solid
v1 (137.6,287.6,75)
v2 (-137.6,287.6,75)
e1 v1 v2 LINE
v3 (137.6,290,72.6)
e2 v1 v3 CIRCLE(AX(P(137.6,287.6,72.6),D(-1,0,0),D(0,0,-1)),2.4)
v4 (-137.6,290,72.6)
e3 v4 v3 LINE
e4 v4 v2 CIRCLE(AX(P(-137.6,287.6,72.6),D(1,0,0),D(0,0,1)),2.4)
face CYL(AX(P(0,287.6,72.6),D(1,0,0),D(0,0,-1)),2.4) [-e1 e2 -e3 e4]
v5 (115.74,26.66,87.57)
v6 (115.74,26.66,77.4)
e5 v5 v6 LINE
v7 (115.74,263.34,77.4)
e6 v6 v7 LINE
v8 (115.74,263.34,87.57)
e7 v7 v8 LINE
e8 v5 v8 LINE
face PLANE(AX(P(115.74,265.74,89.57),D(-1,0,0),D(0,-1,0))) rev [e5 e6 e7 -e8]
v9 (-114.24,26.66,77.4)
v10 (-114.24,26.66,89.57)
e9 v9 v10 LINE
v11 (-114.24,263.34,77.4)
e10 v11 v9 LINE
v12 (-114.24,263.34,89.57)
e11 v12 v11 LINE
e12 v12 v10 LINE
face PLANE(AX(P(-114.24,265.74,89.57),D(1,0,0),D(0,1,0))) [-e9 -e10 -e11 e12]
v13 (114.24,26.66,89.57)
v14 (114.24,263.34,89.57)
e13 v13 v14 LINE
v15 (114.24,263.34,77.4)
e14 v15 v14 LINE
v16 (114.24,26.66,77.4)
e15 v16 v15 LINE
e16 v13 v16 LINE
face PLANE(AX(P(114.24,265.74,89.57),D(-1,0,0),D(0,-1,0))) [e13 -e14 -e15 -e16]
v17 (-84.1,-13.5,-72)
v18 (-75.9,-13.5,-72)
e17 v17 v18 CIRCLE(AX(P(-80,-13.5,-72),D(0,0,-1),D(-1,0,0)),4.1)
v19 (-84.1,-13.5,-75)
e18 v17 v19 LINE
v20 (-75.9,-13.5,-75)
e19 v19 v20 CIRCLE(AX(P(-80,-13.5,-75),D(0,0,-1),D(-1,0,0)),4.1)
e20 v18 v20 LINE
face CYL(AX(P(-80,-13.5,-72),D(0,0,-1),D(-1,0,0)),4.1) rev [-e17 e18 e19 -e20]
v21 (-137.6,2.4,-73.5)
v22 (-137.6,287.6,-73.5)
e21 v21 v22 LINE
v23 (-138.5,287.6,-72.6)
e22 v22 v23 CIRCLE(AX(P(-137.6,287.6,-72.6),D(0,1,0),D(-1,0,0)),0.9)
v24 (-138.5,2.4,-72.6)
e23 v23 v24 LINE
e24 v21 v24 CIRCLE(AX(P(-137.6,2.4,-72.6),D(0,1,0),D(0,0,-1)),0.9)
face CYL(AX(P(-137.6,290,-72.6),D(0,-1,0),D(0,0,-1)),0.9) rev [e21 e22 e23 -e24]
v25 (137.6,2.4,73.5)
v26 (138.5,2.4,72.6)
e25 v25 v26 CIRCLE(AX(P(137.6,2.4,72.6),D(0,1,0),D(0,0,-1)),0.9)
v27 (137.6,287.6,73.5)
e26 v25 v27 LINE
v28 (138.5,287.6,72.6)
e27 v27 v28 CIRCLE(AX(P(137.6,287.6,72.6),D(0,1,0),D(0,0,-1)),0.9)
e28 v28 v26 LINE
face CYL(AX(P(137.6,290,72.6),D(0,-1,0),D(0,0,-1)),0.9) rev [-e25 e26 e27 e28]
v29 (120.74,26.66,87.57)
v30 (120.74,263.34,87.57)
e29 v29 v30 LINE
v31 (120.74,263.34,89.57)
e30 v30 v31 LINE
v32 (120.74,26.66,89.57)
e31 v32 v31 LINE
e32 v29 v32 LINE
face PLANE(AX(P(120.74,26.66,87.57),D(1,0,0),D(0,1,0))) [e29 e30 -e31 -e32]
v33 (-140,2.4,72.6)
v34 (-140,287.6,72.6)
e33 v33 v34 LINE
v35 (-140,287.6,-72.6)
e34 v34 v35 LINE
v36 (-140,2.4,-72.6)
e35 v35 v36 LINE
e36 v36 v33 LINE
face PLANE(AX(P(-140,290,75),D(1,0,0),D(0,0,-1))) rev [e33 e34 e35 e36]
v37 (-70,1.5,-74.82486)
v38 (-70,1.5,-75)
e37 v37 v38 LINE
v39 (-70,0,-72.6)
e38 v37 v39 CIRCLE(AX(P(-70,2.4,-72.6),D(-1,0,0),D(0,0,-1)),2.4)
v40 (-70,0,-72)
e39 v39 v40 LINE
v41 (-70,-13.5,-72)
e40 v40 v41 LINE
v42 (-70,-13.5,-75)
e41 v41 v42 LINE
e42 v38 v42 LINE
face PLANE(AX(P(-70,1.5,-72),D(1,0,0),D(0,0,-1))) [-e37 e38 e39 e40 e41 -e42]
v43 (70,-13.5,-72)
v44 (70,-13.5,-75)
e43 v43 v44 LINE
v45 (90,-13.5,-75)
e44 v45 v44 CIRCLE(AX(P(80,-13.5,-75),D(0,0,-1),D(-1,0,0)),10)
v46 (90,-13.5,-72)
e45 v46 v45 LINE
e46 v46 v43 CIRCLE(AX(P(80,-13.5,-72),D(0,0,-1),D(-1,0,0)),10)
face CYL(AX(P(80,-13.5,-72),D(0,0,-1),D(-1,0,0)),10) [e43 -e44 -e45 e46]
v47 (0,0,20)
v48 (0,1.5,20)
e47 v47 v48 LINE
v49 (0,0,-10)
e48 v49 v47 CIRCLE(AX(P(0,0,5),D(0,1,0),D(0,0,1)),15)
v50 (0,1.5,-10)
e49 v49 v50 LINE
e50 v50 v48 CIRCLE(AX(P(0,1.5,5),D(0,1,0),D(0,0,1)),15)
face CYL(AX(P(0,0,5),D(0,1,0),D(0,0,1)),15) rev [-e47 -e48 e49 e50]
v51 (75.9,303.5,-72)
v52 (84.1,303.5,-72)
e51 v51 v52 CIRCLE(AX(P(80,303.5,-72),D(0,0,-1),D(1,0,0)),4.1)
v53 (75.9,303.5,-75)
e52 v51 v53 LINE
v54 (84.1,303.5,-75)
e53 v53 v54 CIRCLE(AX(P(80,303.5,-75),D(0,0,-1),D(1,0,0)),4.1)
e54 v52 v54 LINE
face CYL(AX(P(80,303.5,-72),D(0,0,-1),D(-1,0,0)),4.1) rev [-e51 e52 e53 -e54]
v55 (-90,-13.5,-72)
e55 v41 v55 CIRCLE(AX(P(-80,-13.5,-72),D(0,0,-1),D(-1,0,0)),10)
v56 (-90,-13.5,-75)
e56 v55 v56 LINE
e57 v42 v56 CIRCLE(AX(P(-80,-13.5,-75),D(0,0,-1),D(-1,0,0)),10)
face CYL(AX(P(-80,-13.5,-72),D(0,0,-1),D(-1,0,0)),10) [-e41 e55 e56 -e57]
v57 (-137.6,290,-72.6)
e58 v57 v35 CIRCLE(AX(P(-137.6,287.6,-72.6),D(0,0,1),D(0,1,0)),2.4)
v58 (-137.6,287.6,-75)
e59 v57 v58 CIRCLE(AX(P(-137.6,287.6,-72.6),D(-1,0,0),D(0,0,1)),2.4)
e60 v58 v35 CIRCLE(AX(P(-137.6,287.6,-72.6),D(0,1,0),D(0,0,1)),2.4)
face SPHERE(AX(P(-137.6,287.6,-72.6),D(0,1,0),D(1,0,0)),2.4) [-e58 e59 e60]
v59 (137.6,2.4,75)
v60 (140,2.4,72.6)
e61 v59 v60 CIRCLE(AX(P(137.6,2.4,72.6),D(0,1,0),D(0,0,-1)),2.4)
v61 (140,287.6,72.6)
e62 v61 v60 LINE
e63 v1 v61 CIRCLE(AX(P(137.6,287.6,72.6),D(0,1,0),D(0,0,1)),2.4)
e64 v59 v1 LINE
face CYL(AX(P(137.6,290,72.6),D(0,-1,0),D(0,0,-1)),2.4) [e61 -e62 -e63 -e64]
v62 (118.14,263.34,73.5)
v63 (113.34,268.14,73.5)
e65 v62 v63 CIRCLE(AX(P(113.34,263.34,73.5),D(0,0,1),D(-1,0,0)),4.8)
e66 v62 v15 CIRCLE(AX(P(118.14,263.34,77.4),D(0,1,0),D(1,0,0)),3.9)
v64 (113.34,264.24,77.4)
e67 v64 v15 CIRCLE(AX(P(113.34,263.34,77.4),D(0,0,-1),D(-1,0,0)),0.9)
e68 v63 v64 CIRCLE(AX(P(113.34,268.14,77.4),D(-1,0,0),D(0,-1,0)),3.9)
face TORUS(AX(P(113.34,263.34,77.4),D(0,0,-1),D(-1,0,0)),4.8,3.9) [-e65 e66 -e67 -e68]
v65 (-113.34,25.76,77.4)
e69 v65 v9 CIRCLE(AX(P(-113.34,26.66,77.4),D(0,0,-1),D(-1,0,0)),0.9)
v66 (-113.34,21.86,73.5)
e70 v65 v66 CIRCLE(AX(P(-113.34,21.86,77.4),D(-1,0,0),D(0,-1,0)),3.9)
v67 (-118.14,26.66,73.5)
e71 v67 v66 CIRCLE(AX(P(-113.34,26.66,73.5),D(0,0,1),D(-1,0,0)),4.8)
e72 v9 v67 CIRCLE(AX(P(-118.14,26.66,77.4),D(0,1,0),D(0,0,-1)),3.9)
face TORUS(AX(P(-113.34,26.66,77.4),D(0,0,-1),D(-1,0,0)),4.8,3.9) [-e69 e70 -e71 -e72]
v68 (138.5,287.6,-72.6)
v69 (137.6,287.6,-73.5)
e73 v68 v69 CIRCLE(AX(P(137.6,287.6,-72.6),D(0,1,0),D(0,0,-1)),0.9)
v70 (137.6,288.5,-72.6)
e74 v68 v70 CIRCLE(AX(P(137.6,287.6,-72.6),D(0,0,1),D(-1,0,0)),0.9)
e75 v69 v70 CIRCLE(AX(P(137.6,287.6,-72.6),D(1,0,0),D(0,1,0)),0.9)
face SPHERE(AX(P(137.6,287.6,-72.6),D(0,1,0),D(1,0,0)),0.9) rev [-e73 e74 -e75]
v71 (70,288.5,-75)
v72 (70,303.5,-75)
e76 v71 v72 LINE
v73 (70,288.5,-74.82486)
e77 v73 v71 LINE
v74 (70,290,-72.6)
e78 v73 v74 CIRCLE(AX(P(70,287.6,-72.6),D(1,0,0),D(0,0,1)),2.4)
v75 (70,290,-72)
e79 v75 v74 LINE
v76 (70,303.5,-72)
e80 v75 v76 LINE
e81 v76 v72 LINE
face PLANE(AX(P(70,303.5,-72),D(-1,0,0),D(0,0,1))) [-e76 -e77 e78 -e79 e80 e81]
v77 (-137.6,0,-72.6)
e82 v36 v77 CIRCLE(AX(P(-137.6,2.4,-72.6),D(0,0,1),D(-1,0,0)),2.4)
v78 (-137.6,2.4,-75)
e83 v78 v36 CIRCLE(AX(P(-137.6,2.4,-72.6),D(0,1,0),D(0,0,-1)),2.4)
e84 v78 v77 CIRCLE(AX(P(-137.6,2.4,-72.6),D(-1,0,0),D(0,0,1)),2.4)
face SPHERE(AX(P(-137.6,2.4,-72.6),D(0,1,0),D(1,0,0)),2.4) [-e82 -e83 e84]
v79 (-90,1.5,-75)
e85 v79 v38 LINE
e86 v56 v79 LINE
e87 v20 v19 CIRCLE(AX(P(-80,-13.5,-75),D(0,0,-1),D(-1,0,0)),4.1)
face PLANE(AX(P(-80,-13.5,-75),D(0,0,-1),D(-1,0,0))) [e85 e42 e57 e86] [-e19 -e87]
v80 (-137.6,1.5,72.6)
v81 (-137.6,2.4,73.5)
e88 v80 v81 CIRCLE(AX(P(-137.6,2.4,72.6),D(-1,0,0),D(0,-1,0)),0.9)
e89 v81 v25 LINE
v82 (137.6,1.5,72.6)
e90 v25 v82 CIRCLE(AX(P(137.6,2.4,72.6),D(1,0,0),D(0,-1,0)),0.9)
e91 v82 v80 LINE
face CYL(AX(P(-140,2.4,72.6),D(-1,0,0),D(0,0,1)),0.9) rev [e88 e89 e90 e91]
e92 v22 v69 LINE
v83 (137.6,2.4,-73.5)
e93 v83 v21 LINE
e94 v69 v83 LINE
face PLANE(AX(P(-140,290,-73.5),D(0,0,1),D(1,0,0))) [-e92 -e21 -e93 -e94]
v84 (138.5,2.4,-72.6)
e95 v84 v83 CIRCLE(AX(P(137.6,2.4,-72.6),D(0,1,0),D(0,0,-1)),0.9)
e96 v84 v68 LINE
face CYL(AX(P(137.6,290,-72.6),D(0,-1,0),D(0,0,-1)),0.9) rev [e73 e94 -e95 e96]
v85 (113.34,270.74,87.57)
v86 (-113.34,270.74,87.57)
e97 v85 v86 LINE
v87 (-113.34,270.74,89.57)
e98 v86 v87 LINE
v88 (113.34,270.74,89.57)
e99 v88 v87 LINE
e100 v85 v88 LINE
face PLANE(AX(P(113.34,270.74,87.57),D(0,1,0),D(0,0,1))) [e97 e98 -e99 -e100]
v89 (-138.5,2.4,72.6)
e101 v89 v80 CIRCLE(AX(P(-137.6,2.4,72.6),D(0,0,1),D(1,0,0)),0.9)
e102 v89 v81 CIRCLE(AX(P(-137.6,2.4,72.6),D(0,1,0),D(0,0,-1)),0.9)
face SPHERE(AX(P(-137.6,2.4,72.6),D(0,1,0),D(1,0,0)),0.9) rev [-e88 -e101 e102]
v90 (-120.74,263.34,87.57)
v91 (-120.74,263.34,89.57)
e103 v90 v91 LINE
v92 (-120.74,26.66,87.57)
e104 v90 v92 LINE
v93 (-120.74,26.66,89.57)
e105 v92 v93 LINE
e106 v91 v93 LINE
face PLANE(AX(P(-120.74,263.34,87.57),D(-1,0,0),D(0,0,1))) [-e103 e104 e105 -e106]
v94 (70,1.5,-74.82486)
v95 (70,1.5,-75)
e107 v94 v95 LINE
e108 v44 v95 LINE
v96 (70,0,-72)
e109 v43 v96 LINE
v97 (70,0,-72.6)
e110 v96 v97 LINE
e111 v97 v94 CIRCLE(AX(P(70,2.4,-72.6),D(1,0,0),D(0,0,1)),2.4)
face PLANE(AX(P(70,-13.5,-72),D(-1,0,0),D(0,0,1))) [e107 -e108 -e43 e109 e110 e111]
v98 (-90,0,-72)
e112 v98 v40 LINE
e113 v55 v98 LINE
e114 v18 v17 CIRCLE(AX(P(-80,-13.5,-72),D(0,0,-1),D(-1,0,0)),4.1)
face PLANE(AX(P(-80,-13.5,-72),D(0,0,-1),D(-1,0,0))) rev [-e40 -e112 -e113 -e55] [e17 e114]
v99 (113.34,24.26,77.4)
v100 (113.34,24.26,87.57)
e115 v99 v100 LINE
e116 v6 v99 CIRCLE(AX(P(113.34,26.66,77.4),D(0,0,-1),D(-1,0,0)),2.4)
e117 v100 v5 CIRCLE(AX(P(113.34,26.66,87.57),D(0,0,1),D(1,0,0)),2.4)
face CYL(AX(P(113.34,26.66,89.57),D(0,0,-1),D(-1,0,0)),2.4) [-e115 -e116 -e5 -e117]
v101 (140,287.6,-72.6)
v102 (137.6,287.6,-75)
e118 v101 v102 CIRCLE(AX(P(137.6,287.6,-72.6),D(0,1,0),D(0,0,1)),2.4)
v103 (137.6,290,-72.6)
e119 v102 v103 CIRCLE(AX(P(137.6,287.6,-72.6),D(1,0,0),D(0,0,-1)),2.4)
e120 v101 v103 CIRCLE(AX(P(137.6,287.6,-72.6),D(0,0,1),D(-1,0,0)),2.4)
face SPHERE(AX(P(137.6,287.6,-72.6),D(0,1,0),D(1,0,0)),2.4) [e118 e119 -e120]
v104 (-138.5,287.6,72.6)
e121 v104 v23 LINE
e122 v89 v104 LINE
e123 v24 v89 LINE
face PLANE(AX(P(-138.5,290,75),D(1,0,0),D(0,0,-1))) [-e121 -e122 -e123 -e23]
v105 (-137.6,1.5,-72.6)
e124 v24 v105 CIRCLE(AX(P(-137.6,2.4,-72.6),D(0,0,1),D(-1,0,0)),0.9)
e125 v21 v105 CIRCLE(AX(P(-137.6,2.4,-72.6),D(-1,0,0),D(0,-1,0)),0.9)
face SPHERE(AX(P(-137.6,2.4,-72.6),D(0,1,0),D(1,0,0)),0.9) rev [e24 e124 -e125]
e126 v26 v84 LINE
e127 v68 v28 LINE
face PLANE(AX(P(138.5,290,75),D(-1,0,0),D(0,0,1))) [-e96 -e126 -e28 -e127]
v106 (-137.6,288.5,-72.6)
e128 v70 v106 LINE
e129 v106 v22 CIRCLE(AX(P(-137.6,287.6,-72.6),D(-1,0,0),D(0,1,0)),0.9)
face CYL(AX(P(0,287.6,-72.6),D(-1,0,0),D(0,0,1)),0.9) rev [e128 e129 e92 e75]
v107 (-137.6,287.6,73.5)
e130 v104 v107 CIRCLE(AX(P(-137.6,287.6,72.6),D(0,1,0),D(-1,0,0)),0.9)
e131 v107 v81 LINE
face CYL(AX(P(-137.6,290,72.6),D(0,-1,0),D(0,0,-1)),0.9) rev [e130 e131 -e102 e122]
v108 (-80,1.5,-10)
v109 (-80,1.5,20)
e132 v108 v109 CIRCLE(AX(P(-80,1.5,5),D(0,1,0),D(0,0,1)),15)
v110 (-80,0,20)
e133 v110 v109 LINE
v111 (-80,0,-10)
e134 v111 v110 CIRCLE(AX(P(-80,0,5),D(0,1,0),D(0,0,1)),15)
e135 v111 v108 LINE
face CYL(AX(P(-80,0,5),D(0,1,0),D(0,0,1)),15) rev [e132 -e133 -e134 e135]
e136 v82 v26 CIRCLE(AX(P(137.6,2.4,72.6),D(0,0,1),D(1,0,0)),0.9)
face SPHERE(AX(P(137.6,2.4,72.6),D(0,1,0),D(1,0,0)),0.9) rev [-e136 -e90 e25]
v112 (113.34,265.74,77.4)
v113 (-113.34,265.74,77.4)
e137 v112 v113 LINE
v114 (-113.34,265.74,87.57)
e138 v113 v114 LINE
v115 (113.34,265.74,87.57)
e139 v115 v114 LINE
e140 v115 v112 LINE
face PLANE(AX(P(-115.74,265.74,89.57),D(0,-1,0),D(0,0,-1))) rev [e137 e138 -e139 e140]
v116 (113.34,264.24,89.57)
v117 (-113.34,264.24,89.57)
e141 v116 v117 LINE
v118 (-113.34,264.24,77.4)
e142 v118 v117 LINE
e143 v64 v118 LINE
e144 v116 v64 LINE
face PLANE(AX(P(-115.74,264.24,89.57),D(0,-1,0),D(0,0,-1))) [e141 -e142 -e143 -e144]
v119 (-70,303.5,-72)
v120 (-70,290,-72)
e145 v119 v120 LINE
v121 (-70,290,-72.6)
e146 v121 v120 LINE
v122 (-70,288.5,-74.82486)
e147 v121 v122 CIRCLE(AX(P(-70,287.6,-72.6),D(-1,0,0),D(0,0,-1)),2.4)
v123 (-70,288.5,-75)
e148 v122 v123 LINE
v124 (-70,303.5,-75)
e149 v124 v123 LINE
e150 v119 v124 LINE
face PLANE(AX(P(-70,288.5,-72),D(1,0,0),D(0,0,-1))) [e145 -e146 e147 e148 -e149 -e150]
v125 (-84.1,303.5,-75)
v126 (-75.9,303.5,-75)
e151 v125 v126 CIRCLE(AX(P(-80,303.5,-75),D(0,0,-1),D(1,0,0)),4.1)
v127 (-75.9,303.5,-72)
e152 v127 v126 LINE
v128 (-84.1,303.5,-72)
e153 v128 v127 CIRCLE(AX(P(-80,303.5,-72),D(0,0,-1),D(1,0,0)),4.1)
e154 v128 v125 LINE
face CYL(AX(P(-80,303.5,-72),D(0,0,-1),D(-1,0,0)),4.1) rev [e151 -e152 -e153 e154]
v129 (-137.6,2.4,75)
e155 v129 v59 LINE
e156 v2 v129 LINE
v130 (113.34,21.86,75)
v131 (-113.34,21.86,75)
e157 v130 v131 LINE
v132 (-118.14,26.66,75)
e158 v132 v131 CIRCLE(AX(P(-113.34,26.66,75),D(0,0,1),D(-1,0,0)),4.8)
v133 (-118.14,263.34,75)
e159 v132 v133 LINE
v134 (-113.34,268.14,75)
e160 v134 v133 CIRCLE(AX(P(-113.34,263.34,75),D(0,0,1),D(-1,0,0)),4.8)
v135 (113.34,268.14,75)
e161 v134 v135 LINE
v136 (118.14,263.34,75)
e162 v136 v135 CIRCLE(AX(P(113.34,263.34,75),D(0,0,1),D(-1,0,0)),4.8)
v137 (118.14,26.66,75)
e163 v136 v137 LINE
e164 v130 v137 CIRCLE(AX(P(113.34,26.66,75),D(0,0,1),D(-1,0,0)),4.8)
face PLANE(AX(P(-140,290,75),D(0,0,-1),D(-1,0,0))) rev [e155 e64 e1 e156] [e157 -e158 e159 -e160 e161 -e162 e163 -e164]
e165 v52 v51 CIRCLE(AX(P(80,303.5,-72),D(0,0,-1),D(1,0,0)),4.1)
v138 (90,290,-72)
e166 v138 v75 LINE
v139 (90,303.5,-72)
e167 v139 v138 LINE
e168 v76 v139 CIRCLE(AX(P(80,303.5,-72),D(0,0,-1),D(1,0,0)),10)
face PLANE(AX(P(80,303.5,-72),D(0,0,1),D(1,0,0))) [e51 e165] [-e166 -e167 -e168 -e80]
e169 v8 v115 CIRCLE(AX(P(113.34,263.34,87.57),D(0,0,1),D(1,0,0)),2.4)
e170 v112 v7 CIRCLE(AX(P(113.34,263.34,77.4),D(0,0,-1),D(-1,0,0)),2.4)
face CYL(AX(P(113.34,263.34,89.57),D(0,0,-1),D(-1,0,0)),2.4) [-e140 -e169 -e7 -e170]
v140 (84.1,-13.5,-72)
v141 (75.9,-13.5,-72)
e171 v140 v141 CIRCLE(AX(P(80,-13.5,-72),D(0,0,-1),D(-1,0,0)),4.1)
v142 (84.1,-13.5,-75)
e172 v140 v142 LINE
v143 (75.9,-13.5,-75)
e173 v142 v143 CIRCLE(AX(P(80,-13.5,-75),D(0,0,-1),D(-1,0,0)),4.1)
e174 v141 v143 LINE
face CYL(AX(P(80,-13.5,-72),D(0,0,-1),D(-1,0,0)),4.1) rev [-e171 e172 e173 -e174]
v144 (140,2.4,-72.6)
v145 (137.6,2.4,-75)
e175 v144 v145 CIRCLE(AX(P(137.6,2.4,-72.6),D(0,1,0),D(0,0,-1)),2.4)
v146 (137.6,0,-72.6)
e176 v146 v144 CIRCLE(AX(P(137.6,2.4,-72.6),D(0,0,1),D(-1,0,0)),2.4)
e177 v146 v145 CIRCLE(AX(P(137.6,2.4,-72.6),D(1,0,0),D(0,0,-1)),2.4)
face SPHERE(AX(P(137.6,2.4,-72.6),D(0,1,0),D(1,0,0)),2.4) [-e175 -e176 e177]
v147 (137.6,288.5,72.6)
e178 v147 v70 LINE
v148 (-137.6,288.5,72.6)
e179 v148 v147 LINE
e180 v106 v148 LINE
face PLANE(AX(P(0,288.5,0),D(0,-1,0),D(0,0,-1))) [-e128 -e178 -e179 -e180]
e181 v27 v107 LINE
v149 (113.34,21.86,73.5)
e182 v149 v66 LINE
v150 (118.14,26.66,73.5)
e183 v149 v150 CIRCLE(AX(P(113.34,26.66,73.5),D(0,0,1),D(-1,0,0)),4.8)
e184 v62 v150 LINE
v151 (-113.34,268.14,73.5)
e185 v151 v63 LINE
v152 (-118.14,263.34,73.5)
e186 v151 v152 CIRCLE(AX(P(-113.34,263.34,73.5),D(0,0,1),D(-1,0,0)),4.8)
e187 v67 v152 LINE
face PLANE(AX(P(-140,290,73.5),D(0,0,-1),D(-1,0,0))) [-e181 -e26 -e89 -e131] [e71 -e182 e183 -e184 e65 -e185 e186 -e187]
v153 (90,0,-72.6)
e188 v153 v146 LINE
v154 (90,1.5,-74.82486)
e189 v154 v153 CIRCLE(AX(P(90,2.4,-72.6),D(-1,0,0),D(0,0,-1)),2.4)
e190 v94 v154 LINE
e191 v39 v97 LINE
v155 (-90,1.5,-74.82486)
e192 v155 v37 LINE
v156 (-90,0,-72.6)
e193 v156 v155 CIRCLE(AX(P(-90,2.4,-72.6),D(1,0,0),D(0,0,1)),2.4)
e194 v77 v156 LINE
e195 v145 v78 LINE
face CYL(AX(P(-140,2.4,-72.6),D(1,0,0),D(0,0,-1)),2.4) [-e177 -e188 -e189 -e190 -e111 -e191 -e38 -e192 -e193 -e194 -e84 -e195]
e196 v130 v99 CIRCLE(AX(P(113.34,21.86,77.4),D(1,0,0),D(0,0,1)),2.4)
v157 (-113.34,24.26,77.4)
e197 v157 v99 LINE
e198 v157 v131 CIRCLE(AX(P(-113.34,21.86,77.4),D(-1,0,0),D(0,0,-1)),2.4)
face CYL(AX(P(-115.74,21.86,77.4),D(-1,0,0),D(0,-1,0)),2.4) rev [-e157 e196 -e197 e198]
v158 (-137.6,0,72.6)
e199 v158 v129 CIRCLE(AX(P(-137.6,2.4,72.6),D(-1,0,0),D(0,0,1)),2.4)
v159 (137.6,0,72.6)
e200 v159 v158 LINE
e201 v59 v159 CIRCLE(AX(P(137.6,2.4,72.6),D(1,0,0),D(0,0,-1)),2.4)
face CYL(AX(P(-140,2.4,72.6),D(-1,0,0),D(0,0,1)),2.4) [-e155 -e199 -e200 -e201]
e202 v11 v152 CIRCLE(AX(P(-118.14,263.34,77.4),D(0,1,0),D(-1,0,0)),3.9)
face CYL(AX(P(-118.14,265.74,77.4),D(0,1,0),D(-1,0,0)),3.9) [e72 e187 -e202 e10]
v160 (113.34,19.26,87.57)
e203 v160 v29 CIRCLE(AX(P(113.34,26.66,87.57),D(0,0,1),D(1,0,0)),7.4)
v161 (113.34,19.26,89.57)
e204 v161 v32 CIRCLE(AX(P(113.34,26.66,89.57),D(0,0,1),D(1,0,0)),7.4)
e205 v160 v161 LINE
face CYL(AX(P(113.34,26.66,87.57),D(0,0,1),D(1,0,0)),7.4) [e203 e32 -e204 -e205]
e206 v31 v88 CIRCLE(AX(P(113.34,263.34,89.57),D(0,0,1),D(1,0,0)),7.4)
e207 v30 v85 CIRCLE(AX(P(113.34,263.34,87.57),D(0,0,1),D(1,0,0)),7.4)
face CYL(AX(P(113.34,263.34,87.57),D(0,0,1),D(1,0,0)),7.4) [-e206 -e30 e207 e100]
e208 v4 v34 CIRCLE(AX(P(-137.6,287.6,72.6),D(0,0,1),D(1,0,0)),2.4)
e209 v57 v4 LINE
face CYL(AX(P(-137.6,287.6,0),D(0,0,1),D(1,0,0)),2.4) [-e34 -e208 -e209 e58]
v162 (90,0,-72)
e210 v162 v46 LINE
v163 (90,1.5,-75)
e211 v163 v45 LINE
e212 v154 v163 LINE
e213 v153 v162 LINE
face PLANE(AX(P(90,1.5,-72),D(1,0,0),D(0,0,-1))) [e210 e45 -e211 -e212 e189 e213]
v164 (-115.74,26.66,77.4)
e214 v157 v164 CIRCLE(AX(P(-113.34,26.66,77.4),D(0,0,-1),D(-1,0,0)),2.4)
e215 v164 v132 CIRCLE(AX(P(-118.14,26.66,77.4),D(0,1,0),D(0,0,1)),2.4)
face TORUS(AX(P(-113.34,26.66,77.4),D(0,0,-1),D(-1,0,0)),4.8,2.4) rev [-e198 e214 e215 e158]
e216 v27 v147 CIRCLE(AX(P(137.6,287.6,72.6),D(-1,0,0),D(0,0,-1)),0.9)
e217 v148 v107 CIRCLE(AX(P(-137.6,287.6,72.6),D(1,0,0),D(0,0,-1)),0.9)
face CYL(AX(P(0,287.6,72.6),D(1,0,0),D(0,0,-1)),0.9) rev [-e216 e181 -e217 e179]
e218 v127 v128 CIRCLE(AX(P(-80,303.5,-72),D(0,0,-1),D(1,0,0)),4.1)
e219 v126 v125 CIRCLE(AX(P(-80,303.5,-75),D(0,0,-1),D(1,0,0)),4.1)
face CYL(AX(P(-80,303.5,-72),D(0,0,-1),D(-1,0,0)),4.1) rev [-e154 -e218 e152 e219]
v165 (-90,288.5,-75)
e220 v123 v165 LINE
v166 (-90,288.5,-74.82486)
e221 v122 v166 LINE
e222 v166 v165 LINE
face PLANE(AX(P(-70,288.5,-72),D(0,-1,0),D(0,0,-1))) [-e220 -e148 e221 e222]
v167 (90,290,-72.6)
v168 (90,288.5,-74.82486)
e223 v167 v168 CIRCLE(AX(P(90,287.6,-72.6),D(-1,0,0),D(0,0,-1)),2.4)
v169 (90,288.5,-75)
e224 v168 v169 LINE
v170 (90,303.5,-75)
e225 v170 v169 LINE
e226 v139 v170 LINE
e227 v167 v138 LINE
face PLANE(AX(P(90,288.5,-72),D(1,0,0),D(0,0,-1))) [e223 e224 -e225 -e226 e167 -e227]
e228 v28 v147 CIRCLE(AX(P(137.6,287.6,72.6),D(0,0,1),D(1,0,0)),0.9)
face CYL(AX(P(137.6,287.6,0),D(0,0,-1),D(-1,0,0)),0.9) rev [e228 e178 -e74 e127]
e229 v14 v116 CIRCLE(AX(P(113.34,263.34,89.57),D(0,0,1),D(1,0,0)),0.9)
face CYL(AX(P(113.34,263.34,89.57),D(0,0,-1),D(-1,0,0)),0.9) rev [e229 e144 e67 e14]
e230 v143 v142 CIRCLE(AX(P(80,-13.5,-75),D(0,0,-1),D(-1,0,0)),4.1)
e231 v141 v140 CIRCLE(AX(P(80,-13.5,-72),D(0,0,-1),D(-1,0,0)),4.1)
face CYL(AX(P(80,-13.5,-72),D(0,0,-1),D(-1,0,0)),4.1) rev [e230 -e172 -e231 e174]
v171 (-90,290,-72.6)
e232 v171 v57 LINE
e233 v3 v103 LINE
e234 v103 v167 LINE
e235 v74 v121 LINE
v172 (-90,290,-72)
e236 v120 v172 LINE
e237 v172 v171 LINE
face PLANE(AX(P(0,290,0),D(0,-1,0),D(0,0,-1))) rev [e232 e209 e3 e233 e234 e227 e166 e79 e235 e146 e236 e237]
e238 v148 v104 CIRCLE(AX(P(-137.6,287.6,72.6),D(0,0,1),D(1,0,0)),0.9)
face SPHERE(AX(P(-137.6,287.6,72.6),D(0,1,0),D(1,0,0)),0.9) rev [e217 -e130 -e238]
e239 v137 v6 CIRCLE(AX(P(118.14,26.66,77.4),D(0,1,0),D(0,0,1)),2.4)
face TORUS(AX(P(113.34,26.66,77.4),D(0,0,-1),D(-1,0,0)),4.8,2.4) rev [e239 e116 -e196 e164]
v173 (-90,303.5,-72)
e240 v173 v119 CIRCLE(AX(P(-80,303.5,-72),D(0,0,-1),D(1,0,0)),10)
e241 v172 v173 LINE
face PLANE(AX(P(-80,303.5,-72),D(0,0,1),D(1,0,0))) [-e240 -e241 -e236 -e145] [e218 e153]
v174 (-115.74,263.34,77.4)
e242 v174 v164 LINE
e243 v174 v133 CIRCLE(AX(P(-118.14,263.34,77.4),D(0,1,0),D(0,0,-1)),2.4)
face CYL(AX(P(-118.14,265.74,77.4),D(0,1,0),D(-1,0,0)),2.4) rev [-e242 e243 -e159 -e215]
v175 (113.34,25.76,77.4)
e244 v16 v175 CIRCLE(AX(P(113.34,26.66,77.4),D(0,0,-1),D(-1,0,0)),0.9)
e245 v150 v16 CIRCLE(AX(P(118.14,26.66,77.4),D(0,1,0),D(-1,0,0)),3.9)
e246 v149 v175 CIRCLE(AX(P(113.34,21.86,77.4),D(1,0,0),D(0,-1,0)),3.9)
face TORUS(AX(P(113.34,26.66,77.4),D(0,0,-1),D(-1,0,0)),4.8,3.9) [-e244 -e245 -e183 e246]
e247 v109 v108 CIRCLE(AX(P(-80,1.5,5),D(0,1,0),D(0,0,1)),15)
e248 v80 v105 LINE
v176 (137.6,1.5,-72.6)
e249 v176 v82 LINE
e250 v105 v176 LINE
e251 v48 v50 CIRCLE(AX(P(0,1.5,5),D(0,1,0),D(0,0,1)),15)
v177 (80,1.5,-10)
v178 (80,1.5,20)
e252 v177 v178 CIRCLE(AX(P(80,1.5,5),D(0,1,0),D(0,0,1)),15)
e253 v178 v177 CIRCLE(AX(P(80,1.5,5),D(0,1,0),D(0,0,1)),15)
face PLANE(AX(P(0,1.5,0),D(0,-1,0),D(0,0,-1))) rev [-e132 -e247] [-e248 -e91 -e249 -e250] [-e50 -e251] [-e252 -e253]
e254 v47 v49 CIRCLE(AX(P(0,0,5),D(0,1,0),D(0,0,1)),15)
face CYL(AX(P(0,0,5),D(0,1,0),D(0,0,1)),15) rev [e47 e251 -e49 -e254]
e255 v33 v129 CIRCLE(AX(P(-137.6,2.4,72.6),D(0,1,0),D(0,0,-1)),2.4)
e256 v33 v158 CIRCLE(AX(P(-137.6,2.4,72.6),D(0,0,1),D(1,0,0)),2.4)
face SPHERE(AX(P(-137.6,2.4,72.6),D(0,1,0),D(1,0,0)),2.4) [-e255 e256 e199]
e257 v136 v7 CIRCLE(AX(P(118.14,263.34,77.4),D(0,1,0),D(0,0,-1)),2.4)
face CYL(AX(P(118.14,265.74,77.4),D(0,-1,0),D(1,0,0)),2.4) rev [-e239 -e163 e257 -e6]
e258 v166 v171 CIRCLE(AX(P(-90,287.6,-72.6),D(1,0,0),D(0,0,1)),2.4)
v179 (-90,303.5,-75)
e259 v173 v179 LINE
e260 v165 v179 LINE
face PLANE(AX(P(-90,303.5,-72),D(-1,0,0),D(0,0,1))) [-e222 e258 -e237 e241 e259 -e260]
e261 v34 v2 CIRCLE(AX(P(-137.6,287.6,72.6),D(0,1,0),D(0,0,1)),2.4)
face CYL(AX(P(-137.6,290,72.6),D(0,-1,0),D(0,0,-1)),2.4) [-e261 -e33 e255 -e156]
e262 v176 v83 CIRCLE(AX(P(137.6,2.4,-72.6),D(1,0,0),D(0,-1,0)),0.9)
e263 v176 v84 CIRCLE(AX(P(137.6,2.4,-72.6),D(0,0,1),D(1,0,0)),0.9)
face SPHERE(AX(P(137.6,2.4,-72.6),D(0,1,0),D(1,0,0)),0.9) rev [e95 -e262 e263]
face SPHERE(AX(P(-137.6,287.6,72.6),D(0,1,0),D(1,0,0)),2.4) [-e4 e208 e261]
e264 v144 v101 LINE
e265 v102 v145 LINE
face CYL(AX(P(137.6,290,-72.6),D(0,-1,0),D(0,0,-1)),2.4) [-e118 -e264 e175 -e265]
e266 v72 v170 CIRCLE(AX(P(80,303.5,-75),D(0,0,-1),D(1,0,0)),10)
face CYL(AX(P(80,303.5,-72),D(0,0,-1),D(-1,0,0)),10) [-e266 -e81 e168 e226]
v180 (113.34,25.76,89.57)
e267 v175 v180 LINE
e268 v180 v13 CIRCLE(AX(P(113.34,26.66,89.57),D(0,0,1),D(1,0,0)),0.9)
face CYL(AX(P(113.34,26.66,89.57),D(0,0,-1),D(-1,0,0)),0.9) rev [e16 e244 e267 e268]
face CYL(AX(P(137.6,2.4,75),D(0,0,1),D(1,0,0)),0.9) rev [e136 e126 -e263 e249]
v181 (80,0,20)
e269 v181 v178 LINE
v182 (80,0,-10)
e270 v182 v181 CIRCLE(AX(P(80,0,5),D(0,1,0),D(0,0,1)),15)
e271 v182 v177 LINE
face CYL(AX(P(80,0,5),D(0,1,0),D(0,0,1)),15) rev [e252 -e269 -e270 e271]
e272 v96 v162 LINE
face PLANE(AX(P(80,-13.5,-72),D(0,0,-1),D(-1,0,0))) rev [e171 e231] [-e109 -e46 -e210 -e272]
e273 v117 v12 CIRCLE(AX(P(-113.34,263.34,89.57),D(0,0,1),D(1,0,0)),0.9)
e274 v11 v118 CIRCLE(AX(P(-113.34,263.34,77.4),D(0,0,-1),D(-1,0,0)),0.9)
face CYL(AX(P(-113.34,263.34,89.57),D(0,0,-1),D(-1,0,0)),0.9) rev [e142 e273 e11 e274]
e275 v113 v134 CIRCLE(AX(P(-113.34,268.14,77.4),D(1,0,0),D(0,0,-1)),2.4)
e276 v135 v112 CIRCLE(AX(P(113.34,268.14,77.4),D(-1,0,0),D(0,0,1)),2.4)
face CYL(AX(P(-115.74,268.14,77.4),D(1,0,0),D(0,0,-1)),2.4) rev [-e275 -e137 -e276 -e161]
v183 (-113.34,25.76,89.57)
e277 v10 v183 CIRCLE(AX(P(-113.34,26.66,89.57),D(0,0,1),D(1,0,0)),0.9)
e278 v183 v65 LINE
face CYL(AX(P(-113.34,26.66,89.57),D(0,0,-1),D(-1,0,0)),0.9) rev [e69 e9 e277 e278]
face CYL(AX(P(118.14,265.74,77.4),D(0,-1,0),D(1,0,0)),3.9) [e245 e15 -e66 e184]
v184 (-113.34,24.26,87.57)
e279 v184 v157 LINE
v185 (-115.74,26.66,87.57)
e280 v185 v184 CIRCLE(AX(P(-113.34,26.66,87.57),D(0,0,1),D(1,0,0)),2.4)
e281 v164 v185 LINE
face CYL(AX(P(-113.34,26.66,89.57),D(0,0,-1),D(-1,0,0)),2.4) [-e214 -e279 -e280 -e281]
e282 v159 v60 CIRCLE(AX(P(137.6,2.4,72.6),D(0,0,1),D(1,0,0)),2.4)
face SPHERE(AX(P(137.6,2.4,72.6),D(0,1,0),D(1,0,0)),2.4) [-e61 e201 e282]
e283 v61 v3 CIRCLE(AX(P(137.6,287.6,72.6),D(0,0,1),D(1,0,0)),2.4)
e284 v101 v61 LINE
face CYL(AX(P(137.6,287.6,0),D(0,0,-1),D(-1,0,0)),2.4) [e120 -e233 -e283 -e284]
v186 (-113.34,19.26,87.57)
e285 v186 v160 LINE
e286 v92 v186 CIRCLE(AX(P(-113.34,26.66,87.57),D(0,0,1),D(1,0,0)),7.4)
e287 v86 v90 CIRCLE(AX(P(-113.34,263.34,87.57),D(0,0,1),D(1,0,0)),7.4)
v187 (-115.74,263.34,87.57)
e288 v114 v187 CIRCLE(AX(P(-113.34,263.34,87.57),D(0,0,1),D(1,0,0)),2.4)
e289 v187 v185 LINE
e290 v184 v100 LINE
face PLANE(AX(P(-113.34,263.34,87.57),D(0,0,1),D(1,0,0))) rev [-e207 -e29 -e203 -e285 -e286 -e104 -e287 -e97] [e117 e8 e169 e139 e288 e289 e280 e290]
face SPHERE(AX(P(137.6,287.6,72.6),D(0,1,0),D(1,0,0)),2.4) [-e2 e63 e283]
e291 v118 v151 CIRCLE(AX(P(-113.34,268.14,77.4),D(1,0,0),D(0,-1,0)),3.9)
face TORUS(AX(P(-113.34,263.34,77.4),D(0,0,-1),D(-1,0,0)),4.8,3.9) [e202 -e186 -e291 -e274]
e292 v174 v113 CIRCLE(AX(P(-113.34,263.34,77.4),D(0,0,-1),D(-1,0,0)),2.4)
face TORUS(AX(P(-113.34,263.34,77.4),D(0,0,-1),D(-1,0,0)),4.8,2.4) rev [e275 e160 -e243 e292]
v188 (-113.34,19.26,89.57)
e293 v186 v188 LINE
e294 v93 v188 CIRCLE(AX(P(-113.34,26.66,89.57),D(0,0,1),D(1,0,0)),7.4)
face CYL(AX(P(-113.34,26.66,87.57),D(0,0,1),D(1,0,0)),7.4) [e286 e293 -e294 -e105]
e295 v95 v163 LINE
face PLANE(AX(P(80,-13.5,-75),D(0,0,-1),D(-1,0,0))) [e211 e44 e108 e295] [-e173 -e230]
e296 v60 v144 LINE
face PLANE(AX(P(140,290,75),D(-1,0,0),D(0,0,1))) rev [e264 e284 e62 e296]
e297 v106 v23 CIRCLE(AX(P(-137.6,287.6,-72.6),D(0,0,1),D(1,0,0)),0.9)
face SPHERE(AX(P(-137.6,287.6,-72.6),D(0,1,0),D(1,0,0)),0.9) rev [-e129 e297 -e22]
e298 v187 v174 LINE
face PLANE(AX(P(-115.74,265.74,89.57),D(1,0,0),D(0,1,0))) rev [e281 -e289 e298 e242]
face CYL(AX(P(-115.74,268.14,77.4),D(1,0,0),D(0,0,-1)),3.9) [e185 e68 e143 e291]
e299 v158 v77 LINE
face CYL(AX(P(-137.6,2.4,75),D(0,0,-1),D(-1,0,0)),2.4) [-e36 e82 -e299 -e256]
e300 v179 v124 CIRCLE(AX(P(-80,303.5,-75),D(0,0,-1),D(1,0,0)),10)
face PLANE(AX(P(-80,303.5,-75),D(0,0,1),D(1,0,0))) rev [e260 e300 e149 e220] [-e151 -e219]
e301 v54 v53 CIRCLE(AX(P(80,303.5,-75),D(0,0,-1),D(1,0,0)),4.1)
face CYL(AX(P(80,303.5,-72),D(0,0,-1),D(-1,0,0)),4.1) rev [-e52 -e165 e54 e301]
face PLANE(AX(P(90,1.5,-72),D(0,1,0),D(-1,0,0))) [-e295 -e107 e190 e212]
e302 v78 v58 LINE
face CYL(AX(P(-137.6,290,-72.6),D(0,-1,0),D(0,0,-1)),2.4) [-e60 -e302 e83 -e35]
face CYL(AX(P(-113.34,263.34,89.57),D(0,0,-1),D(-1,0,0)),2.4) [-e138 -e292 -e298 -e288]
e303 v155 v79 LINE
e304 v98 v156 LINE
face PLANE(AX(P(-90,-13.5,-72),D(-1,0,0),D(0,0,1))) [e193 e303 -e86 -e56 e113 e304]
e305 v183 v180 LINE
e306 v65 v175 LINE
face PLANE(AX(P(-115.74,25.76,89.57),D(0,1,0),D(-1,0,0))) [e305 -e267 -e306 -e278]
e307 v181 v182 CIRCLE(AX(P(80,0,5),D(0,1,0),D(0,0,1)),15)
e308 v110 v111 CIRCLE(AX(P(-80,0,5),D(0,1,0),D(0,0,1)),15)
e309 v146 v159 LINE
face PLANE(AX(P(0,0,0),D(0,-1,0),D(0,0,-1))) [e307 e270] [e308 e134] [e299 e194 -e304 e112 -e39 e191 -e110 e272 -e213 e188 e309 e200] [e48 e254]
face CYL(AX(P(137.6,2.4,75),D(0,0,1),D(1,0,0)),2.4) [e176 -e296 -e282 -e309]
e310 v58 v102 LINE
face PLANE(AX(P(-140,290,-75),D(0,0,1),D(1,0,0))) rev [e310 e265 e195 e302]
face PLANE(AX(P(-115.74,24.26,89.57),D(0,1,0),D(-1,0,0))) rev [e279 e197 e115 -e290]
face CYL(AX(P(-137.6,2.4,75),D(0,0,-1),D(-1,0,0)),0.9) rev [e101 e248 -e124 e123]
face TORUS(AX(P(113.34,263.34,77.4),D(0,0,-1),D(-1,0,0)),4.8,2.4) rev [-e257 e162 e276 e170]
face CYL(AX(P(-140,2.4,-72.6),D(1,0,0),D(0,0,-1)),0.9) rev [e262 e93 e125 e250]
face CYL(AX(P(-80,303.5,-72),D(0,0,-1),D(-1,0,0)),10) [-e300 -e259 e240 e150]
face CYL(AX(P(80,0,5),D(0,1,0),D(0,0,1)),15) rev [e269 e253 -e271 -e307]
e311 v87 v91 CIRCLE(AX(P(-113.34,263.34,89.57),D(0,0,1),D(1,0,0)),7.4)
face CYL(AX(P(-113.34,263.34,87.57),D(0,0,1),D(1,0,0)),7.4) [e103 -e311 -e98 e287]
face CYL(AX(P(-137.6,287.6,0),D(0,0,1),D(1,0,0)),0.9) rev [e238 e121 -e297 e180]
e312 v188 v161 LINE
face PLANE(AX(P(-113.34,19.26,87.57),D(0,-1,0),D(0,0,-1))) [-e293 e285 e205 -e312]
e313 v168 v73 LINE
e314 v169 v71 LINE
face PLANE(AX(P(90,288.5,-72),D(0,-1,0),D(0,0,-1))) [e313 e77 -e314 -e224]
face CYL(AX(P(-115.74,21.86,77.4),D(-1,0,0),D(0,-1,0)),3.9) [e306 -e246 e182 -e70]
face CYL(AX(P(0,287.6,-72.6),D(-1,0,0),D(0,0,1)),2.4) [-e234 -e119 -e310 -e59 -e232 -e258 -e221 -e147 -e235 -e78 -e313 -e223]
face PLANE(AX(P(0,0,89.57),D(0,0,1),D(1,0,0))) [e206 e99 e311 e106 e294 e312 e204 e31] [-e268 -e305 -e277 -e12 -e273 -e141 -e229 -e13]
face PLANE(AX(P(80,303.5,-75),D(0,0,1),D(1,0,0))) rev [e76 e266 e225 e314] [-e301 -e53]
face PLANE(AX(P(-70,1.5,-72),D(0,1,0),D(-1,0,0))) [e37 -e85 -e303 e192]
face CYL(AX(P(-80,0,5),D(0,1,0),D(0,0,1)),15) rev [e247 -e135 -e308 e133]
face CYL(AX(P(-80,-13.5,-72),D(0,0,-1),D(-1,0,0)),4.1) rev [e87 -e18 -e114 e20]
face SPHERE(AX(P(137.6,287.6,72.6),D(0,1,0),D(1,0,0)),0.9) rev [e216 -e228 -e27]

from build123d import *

# Parameters (mm, degrees)
SKETCH_1_W          = 280
SKETCH_1_H          = 150
EXTRUDE_1_DEPTH     = 290
FILLET_1_R          = 2.4
SKETCH_2_W          = 231.48
SKETCH_2_H          = 241.48
EXTRUDE_2_DEPTH     = 14.57
FILLET_2_R          = 2.4
SHELL_1_T           = -1.5
SKETCH_3_R          = 15
CUT_EXTRUDE_1_DEPTH = 333.948997446
SKETCH_4_R          = 4.1
EXTRUDE_3_DEPTH     = 3
EXTRUDE_4_DEPTH     = 2


with BuildPart() as part:
    # 草图1 → 凸台-拉伸1 (new body)
    with BuildSketch(Plane(origin=(0, 0, 0), x_dir=(1, 0, 0), z_dir=(0, 1, 0))):
        Rectangle(SKETCH_1_W, SKETCH_1_H)
    extrude(amount=EXTRUDE_1_DEPTH)

    # 圆角1
    fillet_1_edges = [part.edges().sort_by_distance(p)[0] for p in [
        (-140, 290, 0),
        (0, 290, 75),
        (140, 290, 0),
        (0, 0, 75),
        (-140, 0, 0),
        (0, 0, -75),
        (140, 0, 0),
        (0, 290, -75),
        (140, 145, 75),
        (-140, 145, 75),
        (-140, 145, -75),
        (140, 145, -75),
    ]]
    fillet(fillet_1_edges, radius=FILLET_1_R)

    # 草图2 → 凸台-拉伸2 (add)
    with BuildSketch(Plane.XY.offset(75)):
        with Locations((0, 145)):
            Rectangle(SKETCH_2_W, SKETCH_2_H)
    extrude(amount=EXTRUDE_2_DEPTH)

    # 圆角2
    fillet_2_edges = [part.edges().sort_by_distance(p)[0] for p in [
        (-115.74, 145, 75),
        (-115.74, 265.74, 82.285),
        (0, 24.26, 75),
        (-115.74, 24.26, 82.285),
        (115.74, 145, 75),
        (115.74, 24.26, 82.285),
        (0, 265.74, 75),
        (115.74, 265.74, 82.285),
    ]]
    fillet(fillet_2_edges, radius=FILLET_2_R)

    # 抽壳1
    shell_1_openings = [part.faces().sort_by_distance(p)[0] for p in [
        (0, 145, 89.57),
    ]]
    offset(amount=SHELL_1_T, openings=shell_1_openings, kind=Kind.INTERSECTION)

    # 草图3 → 切除-拉伸1 (cut, through all)
    with BuildSketch(Plane(origin=(0, 1.5, 0), x_dir=(1, 0, 0), z_dir=(0, 1, 0))):
        with Locations(Location((-80, -5, 0), (0, 0, 270))):
            Circle(SKETCH_3_R)
        with Locations(Location((0, -5, 0), (0, 0, 270))):
            Circle(SKETCH_3_R)
        with Locations(Location((80, -5, 0), (0, 0, 270))):
            Circle(SKETCH_3_R)
    extrude(amount=-CUT_EXTRUDE_1_DEPTH, mode=Mode.SUBTRACT)

    # 草图4 → 凸台-拉伸3 (add)
    # profile 1 of 4: a face of its own
    with BuildSketch(Plane(origin=(0, 0, -75), x_dir=(-1, 0, 0), z_dir=(0, 0, -1))):
        with BuildLine():
            Line((-90, 288.5), (-70, 288.5))
            Line((-70, 288.5), (-70, 303.5))
            ThreePointArc((-70, 303.5), (-80, 313.5), (-90, 303.5))
            Line((-90, 303.5), (-90, 288.5))
        make_face()
        with Locations(Location((-80, 303.5, 0), (0, 0, 180))):
            Circle(SKETCH_4_R, mode=Mode.SUBTRACT)
    # profile 2 of 4: a face of its own
    with BuildSketch(Plane(origin=(0, 0, -75), x_dir=(-1, 0, 0), z_dir=(0, 0, -1))):
        with BuildLine():
            Line((-90, 1.5), (-90, -13.5))
            ThreePointArc((-90, -13.5), (-80, -23.5), (-70, -13.5))
            Line((-70, -13.5), (-70, 1.5))
            Line((-70, 1.5), (-90, 1.5))
        make_face()
        with Locations((-80, -13.5)):
            Circle(SKETCH_4_R, mode=Mode.SUBTRACT)
    # profile 3 of 4: a face of its own
    with BuildSketch(Plane(origin=(0, 0, -75), x_dir=(-1, 0, 0), z_dir=(0, 0, -1))):
        with BuildLine():
            Line((70, 1.5), (70, -13.5))
            ThreePointArc((70, -13.5), (80, -23.5), (90, -13.5))
            Line((90, -13.5), (90, 1.5))
            Line((90, 1.5), (70, 1.5))
        make_face()
        with Locations((80, -13.5)):
            Circle(SKETCH_4_R, mode=Mode.SUBTRACT)
    # profile 4 of 4: a face of its own
    with BuildSketch(Plane(origin=(0, 0, -75), x_dir=(-1, 0, 0), z_dir=(0, 0, -1))):
        with BuildLine():
            Line((70, 288.5), (90, 288.5))
            Line((90, 288.5), (90, 303.5))
            ThreePointArc((90, 303.5), (80, 313.5), (70, 303.5))
            Line((70, 303.5), (70, 288.5))
        make_face()
        with Locations(Location((80, 303.5, 0), (0, 0, 180))):
            Circle(SKETCH_4_R, mode=Mode.SUBTRACT)
    extrude(amount=-EXTRUDE_3_DEPTH)

    # 草图5 → 凸台-拉伸4 (add)
    with BuildSketch(Plane.XY.offset(89.57)):
        with BuildLine():
            Line((-120.74, 263.34), (-120.74, 26.66))
            ThreePointArc((-120.74, 26.66), (-118.572590181, 21.427409819), (-113.34, 19.26))
            Line((-113.34, 19.26), (113.34, 19.26))
            ThreePointArc((113.34, 19.26), (118.572590181, 21.427409819), (120.74, 26.66))
            Line((120.74, 26.66), (120.74, 263.34))
            ThreePointArc((120.74, 263.34), (118.572590181, 268.572590181), (113.34, 270.74))
            Line((113.34, 270.74), (-113.34, 270.74))
            ThreePointArc((-113.34, 270.74), (-118.572590181, 268.572590181), (-120.74, 263.34))
        make_face()
        with BuildLine():
            Line((-115.74, 263.34), (-115.74, 26.66))
            ThreePointArc((-115.74, 26.66), (-115.037056275, 24.962943725), (-113.34, 24.26))
            Line((-113.34, 24.26), (113.34, 24.26))
            ThreePointArc((113.34, 24.26), (115.037056275, 24.962943725), (115.74, 26.66))
            Line((115.74, 26.66), (115.74, 263.34))
            ThreePointArc((115.74, 263.34), (115.037056275, 265.037056275), (113.34, 265.74))
            Line((113.34, 265.74), (-113.34, 265.74))
            ThreePointArc((-113.34, 265.74), (-115.037056275, 265.037056275), (-115.74, 263.34))
        make_face(mode=Mode.SUBTRACT)
    extrude(amount=-EXTRUDE_4_DEPTH)


solid = part.part
